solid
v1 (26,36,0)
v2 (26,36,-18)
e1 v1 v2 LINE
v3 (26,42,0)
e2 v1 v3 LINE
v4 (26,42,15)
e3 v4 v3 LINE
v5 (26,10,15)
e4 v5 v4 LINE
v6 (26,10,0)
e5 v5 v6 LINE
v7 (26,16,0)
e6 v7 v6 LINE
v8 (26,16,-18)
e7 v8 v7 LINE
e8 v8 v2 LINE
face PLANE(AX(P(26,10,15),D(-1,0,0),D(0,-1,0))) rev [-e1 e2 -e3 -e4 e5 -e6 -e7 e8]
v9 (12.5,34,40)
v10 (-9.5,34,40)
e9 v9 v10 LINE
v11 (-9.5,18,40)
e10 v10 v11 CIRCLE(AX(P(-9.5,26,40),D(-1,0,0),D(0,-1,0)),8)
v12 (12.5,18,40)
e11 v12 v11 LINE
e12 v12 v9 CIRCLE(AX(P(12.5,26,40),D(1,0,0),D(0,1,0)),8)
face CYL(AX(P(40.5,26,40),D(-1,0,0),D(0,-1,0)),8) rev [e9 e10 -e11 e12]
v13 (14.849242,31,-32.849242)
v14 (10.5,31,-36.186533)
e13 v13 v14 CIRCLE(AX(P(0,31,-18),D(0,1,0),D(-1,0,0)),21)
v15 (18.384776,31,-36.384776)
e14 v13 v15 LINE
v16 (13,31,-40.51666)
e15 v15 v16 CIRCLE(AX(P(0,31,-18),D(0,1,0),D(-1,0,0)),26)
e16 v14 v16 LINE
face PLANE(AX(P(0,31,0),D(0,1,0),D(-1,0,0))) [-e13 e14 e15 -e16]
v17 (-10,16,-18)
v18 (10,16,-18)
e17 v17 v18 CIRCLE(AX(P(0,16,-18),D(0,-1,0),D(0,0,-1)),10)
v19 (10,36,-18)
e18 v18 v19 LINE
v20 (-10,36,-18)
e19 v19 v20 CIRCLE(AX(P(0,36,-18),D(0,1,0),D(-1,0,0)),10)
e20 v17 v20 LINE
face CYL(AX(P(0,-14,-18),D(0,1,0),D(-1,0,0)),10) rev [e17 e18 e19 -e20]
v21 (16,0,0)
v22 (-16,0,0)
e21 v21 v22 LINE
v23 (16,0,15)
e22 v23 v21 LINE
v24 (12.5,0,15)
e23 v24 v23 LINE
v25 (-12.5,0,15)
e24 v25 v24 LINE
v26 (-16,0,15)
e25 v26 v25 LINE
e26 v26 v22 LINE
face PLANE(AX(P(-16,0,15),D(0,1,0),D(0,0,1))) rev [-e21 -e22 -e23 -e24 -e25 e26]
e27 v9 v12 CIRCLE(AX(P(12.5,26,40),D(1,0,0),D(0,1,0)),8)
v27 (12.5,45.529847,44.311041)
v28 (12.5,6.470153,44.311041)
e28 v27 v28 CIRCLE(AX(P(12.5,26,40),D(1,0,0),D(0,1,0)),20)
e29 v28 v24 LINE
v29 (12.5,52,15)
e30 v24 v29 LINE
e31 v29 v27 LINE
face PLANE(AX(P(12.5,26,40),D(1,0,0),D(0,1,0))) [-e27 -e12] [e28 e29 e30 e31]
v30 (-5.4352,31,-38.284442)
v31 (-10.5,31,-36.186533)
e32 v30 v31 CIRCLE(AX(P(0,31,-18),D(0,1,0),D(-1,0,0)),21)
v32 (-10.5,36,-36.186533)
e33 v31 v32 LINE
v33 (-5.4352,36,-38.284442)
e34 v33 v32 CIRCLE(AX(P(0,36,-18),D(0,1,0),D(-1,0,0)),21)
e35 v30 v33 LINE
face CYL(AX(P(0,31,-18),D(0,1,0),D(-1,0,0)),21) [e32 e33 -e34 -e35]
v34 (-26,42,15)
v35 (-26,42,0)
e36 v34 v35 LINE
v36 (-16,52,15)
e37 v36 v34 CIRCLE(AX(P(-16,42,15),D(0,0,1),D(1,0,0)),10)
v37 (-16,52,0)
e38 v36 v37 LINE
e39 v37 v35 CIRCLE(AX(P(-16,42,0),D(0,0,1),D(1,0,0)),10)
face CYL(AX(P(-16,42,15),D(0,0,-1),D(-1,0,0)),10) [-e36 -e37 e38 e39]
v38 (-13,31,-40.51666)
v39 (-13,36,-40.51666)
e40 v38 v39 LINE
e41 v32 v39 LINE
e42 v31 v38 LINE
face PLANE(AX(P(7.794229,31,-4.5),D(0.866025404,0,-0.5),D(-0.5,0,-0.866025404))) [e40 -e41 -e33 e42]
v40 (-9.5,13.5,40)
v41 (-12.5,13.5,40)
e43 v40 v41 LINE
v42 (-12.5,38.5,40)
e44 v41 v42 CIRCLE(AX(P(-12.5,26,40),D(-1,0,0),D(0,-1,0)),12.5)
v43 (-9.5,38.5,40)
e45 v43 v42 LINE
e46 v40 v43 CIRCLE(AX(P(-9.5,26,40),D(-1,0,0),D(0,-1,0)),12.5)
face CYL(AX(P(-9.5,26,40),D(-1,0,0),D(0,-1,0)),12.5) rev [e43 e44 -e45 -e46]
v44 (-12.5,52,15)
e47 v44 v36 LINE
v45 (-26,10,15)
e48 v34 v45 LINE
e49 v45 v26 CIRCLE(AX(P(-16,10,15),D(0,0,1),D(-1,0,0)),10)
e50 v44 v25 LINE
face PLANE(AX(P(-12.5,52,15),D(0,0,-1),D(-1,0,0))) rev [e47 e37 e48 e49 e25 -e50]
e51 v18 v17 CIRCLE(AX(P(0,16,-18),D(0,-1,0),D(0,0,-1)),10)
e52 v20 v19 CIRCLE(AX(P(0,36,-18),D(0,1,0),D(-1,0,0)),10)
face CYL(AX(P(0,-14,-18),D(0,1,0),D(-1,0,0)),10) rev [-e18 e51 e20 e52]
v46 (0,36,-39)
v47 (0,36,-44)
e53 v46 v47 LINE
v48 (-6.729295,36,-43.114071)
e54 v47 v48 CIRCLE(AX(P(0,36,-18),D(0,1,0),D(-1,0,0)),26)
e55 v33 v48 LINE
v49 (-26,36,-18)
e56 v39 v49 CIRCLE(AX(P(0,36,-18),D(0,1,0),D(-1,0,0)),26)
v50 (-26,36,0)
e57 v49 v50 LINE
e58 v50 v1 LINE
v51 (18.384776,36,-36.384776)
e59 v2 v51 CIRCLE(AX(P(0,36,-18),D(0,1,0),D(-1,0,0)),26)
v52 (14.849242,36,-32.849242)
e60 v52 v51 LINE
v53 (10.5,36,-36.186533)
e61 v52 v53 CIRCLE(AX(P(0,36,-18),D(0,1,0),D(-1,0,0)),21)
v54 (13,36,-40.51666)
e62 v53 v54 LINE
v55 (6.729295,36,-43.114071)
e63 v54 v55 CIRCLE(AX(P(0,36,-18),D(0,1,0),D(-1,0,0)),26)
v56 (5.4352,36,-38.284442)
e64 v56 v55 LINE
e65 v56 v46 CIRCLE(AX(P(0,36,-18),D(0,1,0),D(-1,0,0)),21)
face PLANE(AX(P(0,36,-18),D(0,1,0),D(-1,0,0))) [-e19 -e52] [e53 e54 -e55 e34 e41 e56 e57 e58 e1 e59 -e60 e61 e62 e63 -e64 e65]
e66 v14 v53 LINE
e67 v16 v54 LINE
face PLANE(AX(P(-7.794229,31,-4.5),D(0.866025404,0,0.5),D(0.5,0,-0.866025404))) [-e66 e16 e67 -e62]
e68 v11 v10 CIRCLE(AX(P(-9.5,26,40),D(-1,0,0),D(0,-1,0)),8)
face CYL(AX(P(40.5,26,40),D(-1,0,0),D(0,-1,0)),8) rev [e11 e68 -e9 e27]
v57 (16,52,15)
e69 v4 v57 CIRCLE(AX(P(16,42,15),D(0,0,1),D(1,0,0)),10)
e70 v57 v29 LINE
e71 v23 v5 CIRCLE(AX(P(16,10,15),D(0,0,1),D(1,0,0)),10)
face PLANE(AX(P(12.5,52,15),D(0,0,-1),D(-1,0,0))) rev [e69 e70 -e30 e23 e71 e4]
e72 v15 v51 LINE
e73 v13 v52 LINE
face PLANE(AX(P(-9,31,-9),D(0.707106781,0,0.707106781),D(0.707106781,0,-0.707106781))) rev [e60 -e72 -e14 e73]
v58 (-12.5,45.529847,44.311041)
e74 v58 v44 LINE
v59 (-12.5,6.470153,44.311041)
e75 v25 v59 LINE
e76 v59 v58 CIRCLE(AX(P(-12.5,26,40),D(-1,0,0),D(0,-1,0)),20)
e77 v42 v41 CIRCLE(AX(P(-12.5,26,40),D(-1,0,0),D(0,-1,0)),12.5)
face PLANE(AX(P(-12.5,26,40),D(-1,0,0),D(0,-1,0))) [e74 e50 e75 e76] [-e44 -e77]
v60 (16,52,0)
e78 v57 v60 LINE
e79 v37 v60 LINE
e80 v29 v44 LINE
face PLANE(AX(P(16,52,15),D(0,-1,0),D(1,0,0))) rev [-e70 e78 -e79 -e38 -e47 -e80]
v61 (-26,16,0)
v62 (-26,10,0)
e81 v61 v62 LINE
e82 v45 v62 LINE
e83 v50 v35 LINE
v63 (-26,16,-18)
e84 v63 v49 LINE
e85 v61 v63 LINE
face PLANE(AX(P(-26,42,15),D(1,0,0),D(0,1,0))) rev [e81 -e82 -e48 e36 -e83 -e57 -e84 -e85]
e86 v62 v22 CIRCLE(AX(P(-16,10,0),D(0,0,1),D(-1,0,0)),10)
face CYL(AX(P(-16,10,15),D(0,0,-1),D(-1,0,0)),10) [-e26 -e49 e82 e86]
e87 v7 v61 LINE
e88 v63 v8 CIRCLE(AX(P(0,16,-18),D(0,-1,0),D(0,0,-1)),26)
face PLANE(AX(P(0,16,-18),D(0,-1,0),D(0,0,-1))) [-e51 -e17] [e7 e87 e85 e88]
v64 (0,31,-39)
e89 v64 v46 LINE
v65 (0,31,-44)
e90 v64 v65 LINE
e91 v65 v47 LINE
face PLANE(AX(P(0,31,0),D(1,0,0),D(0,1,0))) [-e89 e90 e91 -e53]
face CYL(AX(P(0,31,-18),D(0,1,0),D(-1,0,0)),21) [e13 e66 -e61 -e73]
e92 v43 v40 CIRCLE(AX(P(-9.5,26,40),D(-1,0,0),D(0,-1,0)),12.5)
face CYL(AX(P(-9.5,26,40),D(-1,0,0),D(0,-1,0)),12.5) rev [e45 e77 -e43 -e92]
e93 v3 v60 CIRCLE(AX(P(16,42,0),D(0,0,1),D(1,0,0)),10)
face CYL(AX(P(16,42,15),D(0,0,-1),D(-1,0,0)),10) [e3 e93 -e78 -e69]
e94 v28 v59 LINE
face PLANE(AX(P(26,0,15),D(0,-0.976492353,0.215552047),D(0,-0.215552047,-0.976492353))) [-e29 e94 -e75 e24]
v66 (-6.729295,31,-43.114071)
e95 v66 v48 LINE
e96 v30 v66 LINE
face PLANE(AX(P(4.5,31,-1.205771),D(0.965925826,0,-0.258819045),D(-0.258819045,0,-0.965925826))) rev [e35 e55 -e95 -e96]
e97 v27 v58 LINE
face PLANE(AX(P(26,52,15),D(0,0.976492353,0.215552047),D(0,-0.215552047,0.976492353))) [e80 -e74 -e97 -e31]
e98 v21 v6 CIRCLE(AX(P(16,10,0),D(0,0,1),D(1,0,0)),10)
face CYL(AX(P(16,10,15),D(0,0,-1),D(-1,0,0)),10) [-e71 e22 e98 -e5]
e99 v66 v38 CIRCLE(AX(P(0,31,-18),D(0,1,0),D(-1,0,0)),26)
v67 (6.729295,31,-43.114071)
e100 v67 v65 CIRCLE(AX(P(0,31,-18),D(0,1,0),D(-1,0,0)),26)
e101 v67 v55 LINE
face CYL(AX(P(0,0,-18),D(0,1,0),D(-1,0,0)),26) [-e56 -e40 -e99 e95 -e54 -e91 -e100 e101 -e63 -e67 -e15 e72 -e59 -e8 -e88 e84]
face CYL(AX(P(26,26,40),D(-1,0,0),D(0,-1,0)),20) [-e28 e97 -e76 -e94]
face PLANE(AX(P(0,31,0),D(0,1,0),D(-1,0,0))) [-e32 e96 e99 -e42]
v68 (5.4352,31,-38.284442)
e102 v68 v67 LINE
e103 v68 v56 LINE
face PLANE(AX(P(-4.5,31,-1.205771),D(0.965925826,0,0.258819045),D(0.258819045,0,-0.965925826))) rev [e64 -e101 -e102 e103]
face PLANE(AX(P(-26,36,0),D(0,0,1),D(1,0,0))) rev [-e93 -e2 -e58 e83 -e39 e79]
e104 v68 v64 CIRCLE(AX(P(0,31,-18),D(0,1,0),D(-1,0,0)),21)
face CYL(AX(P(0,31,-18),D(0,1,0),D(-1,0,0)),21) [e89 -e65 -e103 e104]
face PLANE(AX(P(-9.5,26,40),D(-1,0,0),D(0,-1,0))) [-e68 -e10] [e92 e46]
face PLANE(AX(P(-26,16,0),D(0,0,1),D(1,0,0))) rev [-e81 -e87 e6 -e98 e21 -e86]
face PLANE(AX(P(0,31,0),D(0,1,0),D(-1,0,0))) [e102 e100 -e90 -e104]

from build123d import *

# Parameters (mm, degrees)
ROUNDED_BASE_BLOCK_DEPTH   = 15
UPPER_BLOCK_DEPTH          = 52
UPPER_BLOCK_NOTCH_A_DEPTH  = 13.5
UPPER_START                = -13.5
UPPER_BLOCK_NOTCH_B_DEPTH  = 13.5
CROSS_BLOCK_DEPTH          = 52
CROSS_BLOCK_NOTCH_A_DEPTH  = 16
CROSS_START                = -16
CROSS_BLOCK_NOTCH_B_DEPTH  = 16
BORE_NOTCH_TEETH_CUT_DEPTH = 5
CROSS_BORE_10_SKETCH_R     = 10
CROSS_BORE_10_DEPTH        = 50
COUNTERBORE_25_SKETCH_R    = 12.5
COUNTERBORE_25_X3_DEPTH    = 3
MAIN_BORE_16_SKETCH_R      = 8
MAIN_BORE_16_DEPTH         = 50


with BuildPart() as part:
    # Base Block Profile Sketch → Rounded Base Block (new body)
    with BuildSketch(Plane.XY):
        with BuildLine():
            Line((-16, 0), (16, 0))
            ThreePointArc((16, 0), (23.071067812, 2.928932188), (26, 10))
            Line((26, 10), (26, 42))
            ThreePointArc((26, 42), (23.071067812, 49.071067812), (16, 52))
            Line((16, 52), (-16, 52))
            ThreePointArc((-16, 52), (-23.071067812, 49.071067812), (-26, 42))
            Line((-26, 42), (-26, 10))
            ThreePointArc((-26, 10), (-23.071067812, 2.928932188), (-16, 0))
        make_face()
    extrude(amount=ROUNDED_BASE_BLOCK_DEPTH)

    # Upper Block Profile Sketch → Upper Block (add)
    with BuildSketch(Plane.ZY.offset(26)):
        with BuildLine():
            Line((15, 52), (15, 0))
            Line((15, 0), (44.311040938, 6.470152944))
            ThreePointArc((44.311040938, 6.470152944), (60, 26), (44.311040938, 45.529847056))
            Line((44.311040938, 45.529847056), (15, 52))
        make_face()
    extrude(amount=-UPPER_BLOCK_DEPTH)

    # Upper Block Notch A Sketch → Upper Block Notch A (cut)
    with BuildSketch(Plane.ZY.offset(26)):
        with BuildLine():
            Line((15, 52), (44.311040938, 45.529847056))
            ThreePointArc((44.311040938, 45.529847056), (60, 26), (44.311040938, 6.470152944))
            Line((44.311040938, 6.470152944), (15, 0))
            Line((15, 0), (15, 52))
        make_face()
    extrude(amount=-UPPER_BLOCK_NOTCH_A_DEPTH, mode=Mode.SUBTRACT)

    # Upper Block Notch B Sketch → Upper Block Notch B (cut)
    with BuildSketch(Plane(origin=(26, 0, 0), x_dir=(0, 0, -1), z_dir=(1, 0, 0)).offset(UPPER_START)):
        with BuildLine():
            Line((-15, 52), (-15, 0))
            Line((-15, 0), (-44.311040938, 6.470152944))
            ThreePointArc((-44.311040938, 6.470152944), (-60, 26), (-44.311040938, 45.529847056))
            Line((-44.311040938, 45.529847056), (-15, 52))
        make_face()
    extrude(amount=UPPER_BLOCK_NOTCH_B_DEPTH, mode=Mode.SUBTRACT)

    # Cross Block Profile Sketch → Cross Block (add)
    with BuildSketch(Plane(origin=(0, 52, 0), x_dir=(1, 0, 0), z_dir=(0, 1, 0))):
        with BuildLine():
            Line((-26, 0), (-26, 18))
            ThreePointArc((-26, 18), (0, 44), (26, 18))
            Line((26, 18), (26, 0))
            Line((26, 0), (-26, 0))
        make_face()
    extrude(amount=-CROSS_BLOCK_DEPTH)

    # Cross Block Notch A Sketch → Cross Block Notch A (cut)
    with BuildSketch(Plane(origin=(0, 52, 0), x_dir=(1, 0, 0), z_dir=(0, 1, 0))):
        with BuildLine():
            Line((-26, 0), (26, 0))
            Line((26, 0), (26, 18))
            ThreePointArc((26, 18), (0, 44), (-26, 18))
            Line((-26, 18), (-26, 0))
        make_face()
    extrude(amount=-CROSS_BLOCK_NOTCH_A_DEPTH, mode=Mode.SUBTRACT)

    # Cross Block Notch B Sketch → Cross Block Notch B (cut)
    with BuildSketch(Plane.XZ.offset(CROSS_START)):
        with BuildLine():
            Line((-26, 0), (26, 0))
            Line((26, 0), (26, -18))
            ThreePointArc((26, -18), (0, -44), (-26, -18))
            Line((-26, -18), (-26, 0))
        make_face()
    extrude(amount=CROSS_BLOCK_NOTCH_B_DEPTH, mode=Mode.SUBTRACT)

    # Bore Notch Teeth Sketch → Bore Notch Teeth Cut (cut)
    with BuildSketch(Plane(origin=(0, 36, 0), x_dir=(1, 0, 0), z_dir=(0, 1, 0))):
        with BuildLine():
            Line((-5.435199947, 38.284442352), (-6.729295173, 43.114071484))
            ThreePointArc((-6.729295173, 43.114071484), (-9.949769241, 42.020867845), (-13, 40.516660498))
            Line((-13, 40.516660498), (-10.5, 36.186533479))
            ThreePointArc((-10.5, 36.186533479), (-8.03635208, 37.401470183), (-5.435199947, 38.284442352))
        make_face()
        with BuildLine():
            Line((0, 44), (0, 39))
            ThreePointArc((0, 39), (2.741050037, 38.820342089), (5.435199947, 38.284442352))
            Line((5.435199947, 38.284442352), (6.729295173, 43.114071484))
            ThreePointArc((6.729295173, 43.114071484), (3.393680998, 43.777566396), (0, 44))
        make_face()
        with BuildLine():
            ThreePointArc((18.384776311, 36.384776311), (15.827797154, 38.627186848), (13, 40.516660498))
            Line((13, 40.516660498), (10.5, 36.186533479))
            ThreePointArc((10.5, 36.186533479), (12.783990009, 34.660420146), (14.849242405, 32.849242405))
            Line((14.849242405, 32.849242405), (18.384776311, 36.384776311))
        make_face()
    extrude(amount=-BORE_NOTCH_TEETH_CUT_DEPTH, mode=Mode.SUBTRACT)

    # Cross Bore Ø10 Sketch → Cross Bore Ø10 (cut)
    with BuildSketch(Plane(origin=(0, 36, 0), x_dir=(1, 0, 0), z_dir=(0, 1, 0))):
        with Locations(Location((0, 18, 0), (0, 0, 180))):
            Circle(CROSS_BORE_10_SKETCH_R)
    extrude(amount=-CROSS_BORE_10_DEPTH, mode=Mode.SUBTRACT)

    # Counterbore Ø25 Sketch → Counterbore Ø25 x3 (cut)
    with BuildSketch(Plane.ZY.offset(12.5)):
        with Locations(Location((40, 26, 0), (0, 0, 270))):
            Circle(COUNTERBORE_25_SKETCH_R)
    extrude(amount=-COUNTERBORE_25_X3_DEPTH, mode=Mode.SUBTRACT)

    # Main Bore Ø16 Sketch → Main Bore Ø16 (cut)
    with BuildSketch(Plane.ZY.offset(9.5)):
        with Locations(Location((40, 26, 0), (0, 0, 270))):
            Circle(MAIN_BORE_16_SKETCH_R)
    extrude(amount=-MAIN_BORE_16_DEPTH, mode=Mode.SUBTRACT)


solid = part.part
